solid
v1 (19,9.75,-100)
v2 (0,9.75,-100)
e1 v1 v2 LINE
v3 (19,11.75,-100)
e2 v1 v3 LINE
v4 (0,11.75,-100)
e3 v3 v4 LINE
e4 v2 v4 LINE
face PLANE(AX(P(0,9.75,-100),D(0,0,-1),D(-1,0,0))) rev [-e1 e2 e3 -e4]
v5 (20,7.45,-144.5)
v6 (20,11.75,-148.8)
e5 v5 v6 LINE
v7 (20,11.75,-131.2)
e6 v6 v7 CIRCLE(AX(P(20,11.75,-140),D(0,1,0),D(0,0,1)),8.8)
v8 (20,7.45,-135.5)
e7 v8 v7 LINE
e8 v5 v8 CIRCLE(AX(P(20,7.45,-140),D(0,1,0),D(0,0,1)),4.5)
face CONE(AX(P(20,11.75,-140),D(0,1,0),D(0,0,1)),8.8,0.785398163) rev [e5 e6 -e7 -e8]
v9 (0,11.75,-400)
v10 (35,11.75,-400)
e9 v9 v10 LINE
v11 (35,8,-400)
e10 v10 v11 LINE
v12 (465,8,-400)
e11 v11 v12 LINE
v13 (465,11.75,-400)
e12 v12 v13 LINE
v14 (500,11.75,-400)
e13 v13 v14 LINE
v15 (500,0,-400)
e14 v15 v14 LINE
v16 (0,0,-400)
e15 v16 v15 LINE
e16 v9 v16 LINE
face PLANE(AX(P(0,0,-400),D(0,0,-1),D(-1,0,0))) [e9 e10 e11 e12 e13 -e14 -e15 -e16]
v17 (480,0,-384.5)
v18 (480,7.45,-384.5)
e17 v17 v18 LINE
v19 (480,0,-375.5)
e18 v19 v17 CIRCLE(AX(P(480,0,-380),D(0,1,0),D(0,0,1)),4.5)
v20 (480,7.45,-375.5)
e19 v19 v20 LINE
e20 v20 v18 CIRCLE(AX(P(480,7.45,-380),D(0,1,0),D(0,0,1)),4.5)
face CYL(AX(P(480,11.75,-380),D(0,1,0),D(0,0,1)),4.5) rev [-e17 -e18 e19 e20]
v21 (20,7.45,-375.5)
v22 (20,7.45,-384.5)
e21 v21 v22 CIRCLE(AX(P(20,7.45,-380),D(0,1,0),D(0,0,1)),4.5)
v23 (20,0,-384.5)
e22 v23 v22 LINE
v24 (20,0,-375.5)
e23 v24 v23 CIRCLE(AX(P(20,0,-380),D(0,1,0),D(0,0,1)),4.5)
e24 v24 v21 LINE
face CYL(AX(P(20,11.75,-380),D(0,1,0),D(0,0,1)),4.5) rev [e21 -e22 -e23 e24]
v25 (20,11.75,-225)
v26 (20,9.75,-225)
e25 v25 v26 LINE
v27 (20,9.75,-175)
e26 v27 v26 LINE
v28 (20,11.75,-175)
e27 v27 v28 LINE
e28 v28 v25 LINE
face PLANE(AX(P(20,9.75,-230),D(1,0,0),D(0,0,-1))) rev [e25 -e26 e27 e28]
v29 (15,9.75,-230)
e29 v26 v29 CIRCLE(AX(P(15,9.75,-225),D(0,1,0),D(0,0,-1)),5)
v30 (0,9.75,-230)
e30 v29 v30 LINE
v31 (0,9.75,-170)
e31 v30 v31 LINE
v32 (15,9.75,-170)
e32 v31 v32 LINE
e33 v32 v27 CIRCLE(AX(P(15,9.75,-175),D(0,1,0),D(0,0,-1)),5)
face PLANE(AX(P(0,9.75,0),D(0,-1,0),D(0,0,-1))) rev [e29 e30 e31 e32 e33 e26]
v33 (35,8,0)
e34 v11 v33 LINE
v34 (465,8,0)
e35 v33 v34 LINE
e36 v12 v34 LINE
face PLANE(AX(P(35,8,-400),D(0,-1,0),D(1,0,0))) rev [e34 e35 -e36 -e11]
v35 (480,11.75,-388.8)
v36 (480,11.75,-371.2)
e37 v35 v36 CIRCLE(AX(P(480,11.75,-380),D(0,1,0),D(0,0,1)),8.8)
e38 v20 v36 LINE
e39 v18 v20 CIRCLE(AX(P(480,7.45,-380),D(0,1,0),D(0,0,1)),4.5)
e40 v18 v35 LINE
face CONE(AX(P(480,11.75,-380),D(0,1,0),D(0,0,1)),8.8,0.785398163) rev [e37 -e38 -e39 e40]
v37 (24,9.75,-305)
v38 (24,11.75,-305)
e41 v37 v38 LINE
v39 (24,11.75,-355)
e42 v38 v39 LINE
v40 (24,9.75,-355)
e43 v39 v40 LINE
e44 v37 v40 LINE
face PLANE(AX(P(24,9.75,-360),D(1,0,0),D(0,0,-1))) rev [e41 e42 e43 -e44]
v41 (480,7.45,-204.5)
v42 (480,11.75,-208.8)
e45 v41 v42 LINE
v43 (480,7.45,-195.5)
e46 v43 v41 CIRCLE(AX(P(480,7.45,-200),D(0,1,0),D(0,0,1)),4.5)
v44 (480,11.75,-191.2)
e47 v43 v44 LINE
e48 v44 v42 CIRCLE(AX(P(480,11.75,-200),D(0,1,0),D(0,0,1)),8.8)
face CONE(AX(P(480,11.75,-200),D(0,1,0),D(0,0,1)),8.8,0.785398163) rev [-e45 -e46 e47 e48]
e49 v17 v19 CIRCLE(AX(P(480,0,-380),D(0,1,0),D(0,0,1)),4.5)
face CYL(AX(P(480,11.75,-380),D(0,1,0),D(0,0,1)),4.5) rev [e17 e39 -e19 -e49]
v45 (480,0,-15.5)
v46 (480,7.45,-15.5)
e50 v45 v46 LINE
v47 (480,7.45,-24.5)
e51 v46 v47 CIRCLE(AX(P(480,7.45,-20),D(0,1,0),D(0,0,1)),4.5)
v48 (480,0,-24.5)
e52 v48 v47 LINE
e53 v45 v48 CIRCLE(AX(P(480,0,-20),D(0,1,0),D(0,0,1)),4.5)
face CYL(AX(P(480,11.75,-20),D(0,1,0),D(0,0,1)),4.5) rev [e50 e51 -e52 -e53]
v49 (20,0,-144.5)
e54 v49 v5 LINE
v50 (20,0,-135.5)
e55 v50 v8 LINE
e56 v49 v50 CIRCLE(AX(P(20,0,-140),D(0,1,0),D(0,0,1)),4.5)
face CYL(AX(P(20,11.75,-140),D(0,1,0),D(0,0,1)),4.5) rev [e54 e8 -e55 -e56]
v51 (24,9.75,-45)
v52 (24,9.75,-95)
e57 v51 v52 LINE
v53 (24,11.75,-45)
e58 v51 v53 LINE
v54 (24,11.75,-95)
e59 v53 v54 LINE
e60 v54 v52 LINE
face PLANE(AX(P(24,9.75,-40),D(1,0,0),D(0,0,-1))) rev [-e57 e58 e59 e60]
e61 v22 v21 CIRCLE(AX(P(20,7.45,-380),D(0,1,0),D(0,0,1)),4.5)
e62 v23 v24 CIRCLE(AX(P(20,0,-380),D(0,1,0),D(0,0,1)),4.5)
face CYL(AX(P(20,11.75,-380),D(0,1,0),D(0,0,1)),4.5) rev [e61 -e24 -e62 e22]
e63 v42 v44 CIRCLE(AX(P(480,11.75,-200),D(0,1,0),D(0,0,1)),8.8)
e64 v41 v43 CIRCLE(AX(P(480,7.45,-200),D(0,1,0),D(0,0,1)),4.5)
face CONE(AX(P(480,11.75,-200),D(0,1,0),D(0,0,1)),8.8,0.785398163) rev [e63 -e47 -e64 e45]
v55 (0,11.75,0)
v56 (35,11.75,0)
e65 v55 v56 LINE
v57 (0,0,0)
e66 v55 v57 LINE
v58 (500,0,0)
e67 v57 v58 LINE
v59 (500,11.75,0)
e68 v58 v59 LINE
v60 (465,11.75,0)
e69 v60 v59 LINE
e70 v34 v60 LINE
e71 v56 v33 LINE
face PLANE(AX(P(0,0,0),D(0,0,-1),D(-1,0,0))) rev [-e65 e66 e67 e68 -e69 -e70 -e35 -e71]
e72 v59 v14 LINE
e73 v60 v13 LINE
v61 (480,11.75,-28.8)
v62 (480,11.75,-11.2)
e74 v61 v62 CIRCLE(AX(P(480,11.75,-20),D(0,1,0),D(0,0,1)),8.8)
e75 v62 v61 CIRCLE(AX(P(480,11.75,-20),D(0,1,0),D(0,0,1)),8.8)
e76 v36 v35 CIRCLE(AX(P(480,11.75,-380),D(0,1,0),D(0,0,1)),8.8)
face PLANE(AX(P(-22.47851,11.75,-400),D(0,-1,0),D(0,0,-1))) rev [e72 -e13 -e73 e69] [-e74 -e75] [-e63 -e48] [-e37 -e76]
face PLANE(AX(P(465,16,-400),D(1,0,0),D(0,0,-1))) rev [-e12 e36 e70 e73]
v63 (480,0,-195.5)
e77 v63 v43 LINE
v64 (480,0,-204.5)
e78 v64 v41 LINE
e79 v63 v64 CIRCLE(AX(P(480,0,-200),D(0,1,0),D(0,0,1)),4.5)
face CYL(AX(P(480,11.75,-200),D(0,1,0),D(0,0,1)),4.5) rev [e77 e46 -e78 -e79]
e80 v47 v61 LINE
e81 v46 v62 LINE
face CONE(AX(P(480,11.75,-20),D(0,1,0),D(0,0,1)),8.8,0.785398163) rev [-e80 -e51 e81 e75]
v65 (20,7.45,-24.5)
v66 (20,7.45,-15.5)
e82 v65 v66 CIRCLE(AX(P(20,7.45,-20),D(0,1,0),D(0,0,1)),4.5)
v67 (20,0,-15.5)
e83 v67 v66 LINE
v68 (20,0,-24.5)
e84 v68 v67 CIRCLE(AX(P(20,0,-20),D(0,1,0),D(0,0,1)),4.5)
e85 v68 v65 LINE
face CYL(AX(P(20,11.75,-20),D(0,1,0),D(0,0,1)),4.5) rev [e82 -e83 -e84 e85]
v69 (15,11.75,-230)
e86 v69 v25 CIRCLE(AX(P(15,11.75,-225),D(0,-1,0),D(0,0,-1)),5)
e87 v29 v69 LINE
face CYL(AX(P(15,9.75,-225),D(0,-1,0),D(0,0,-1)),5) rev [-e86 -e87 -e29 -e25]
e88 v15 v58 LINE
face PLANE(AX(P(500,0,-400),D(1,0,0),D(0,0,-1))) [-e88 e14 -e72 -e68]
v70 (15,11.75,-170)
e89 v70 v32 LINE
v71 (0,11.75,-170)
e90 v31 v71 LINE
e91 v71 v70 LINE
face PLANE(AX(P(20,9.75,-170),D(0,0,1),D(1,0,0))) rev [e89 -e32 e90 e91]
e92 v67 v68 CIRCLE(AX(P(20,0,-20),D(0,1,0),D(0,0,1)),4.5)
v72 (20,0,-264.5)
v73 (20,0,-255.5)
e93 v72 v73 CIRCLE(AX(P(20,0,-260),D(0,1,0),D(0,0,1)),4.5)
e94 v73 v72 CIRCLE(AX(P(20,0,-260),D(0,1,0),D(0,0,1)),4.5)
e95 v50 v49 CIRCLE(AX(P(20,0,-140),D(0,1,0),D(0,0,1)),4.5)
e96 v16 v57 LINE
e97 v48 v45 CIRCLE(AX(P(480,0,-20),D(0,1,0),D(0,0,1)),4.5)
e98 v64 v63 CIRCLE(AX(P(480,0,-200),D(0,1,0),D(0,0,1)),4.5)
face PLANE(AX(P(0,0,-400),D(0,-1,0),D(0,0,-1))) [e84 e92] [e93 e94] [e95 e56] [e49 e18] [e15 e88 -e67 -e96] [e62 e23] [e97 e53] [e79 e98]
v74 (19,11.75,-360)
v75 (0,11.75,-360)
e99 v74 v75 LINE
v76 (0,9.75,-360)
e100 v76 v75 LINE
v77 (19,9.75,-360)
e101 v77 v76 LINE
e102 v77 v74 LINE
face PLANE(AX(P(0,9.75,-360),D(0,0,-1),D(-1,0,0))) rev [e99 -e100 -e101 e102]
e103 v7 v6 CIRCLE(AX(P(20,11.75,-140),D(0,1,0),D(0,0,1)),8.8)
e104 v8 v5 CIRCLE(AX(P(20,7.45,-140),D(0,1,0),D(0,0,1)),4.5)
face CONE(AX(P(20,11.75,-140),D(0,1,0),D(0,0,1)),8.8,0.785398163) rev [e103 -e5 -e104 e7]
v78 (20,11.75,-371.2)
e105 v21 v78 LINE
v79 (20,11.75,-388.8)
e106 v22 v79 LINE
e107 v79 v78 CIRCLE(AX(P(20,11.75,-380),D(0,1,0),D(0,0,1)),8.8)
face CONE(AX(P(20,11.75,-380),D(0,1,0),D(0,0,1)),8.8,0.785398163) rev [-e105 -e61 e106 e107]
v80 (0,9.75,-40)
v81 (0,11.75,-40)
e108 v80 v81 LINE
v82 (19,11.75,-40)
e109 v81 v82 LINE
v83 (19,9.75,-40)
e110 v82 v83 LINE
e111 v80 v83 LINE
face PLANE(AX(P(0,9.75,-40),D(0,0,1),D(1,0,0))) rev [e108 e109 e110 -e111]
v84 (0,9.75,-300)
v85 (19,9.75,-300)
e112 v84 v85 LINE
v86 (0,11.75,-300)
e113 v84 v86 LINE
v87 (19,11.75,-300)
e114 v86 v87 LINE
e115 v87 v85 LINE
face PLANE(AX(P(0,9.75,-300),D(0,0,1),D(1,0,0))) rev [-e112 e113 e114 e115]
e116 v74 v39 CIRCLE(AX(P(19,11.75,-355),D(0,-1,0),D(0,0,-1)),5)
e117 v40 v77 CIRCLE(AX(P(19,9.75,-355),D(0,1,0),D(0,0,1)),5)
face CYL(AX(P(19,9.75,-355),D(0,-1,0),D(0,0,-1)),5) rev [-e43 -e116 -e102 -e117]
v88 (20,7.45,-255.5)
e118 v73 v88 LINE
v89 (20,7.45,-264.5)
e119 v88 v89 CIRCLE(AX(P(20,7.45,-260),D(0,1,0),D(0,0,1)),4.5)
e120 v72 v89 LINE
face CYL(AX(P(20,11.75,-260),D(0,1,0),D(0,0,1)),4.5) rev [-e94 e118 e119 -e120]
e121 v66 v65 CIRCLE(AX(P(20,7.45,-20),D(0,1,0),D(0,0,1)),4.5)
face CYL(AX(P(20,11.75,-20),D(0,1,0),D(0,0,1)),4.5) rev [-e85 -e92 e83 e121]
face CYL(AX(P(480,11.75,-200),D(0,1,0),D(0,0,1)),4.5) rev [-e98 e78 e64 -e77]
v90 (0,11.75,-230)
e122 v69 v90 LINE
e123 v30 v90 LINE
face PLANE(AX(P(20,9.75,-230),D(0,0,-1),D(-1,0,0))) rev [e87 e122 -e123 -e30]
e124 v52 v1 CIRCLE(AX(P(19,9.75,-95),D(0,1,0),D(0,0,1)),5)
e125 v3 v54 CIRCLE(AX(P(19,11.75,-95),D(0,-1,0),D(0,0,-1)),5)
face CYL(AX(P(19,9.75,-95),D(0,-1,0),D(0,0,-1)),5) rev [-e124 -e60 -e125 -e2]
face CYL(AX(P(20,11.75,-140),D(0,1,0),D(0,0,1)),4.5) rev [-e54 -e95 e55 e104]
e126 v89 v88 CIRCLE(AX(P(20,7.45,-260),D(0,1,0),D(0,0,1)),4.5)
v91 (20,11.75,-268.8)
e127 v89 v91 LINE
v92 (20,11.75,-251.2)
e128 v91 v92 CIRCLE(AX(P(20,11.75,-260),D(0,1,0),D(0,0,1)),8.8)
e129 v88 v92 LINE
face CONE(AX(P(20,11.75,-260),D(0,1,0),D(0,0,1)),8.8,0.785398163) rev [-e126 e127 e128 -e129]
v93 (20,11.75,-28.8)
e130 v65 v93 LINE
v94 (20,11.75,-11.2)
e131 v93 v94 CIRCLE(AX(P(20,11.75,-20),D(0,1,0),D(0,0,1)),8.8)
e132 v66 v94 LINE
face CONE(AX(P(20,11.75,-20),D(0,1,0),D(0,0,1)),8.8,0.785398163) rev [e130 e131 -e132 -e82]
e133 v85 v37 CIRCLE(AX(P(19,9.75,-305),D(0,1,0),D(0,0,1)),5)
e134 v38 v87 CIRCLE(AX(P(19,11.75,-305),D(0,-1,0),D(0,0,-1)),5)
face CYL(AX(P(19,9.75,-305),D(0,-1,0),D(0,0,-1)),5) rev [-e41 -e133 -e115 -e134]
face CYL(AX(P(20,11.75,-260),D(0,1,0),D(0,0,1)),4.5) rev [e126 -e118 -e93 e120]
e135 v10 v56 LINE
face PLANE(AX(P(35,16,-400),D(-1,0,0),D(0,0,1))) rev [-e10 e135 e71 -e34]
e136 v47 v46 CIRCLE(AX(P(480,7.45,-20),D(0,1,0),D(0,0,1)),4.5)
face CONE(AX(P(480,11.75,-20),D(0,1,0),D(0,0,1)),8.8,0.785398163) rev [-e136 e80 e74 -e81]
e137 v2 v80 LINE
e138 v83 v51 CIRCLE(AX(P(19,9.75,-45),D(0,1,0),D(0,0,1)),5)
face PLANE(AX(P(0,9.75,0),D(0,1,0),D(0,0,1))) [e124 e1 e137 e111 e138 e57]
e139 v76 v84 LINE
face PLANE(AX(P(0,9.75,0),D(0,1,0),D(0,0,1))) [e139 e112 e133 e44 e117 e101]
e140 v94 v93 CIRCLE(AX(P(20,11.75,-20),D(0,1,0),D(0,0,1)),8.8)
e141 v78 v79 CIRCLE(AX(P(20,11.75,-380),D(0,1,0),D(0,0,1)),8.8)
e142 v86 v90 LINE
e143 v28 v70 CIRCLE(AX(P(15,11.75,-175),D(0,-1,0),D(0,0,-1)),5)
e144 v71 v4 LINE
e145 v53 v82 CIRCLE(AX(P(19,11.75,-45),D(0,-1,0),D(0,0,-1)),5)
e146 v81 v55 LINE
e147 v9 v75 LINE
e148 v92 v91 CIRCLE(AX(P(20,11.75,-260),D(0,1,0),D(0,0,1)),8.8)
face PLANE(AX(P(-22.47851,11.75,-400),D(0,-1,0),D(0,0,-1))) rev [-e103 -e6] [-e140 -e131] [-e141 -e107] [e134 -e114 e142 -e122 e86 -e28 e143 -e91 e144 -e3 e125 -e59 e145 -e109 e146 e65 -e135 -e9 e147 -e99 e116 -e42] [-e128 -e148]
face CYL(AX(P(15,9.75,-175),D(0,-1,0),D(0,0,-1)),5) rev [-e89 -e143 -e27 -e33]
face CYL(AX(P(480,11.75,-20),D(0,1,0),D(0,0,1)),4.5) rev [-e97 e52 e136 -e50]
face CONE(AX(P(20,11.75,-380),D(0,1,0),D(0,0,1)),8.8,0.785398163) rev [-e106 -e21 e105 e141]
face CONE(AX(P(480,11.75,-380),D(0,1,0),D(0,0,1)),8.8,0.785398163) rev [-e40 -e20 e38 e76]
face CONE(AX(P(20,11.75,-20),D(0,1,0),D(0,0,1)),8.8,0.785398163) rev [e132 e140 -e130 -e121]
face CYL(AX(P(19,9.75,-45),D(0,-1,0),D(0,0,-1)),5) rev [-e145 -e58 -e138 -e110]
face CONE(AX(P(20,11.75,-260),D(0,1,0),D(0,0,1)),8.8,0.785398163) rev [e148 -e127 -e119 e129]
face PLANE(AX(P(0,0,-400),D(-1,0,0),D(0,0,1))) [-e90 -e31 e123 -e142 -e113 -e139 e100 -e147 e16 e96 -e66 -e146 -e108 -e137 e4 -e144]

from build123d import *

# Parameters (mm, degrees)
SKETCH1_W                                           = 500
SKETCH1_H                                           = 24
BOSS_EXTRUDE1_DEPTH                                 = 400
SKETCH2_W                                           = 430
SKETCH2_H                                           = 8
CUT_EXTRUDE1_DEPTH                                  = 641.762046317
SKETCH3_W                                           = 544.957019416
SKETCH3_H                                           = 0.5
CUT_EXTRUDE2_DEPTH                                  = 641.762046317
SKETCH12_W                                          = 569.007892772
SKETCH12_H                                          = 39.328779912
CUT_EXTRUDE3_DEPTH                                  = 641.762046317
HOLE_WIZARD_HEX_SOCKET_SEMI_COUNTERSUNK_D           = 9
HOLE_WIZARD_HEX_SOCKET_SEMI_COUNTERSUNK_CSINK_D     = 17.6
HOLE_WIZARD_HEX_SOCKET_SEMI_COUNTERSUNK_CSINK_ANGLE = 90
SKETCH16_W                                          = 24
SKETCH16_H                                          = 60
SKETCH16_W_2                                        = 20
CUT_EXTRUDE4_DEPTH                                  = 2
FILLET1_R                                           = 5
HOLE_WIZARD_HEX_SOCKET_SEMI_COUNTER_2_D             = 9
HOLE_WIZARD_HEX_SOCKET_SEMI_COUNTER_2_CSINK_D       = 17.6
HOLE_WIZARD_HEX_SOCKET_SEMI_COUNTER_2_CSINK_ANGLE   = 90


with BuildPart() as part:
    # Sketch1 → Boss-Extrude1 (new body)
    with BuildSketch(Plane.XY):
        with Locations((250, 12)):
            Rectangle(SKETCH1_W, SKETCH1_H)
    extrude(amount=-BOSS_EXTRUDE1_DEPTH)

    # Sketch2 → Cut-Extrude1 (cut, through all)
    with BuildSketch(Plane.XY):
        with Locations((250, 12)):
            Rectangle(SKETCH2_W, SKETCH2_H)
    extrude(amount=-CUT_EXTRUDE1_DEPTH, mode=Mode.SUBTRACT)

    # Sketch3 → Cut-Extrude2 (cut, through all)
    with BuildSketch(Plane.XY):
        with Locations((250, 12)):
            Rectangle(SKETCH3_W, SKETCH3_H)
    extrude(amount=-CUT_EXTRUDE2_DEPTH, mode=Mode.SUBTRACT)


with BuildPart() as cut_extrude2_piece_1:
    # of the separate pieces the step leaves, piece 1, a body of its own (cut_extrude2_pieces)
    add(part.part.solids().sort_by_distance((0, 0, 0))[0])

    # Hole wizard_ hex socket semi-countersunk (through all)
    with Locations(Plane(origin=(0, 11.75, 0), x_dir=(1, 0, 0), z_dir=(0, 1, 0))):
        with Locations((20, 20), (480, 20), (20, 380), (480, 380)):
            CounterSinkHole(HOLE_WIZARD_HEX_SOCKET_SEMI_COUNTERSUNK_D / 2, HOLE_WIZARD_HEX_SOCKET_SEMI_COUNTERSUNK_CSINK_D / 2, counter_sink_angle=HOLE_WIZARD_HEX_SOCKET_SEMI_COUNTERSUNK_CSINK_ANGLE)

    # Sketch16 → Cut-Extrude4 (cut)
    with BuildSketch(Plane(origin=(0, 11.75, 0), x_dir=(1, 0, 0), z_dir=(0, 1, 0))):
        with Locations((12, 330)):
            Rectangle(SKETCH16_W, SKETCH16_H)
        with Locations((12, 70)):
            Rectangle(SKETCH16_W, SKETCH16_H)
        with Locations((10, 200)):
            Rectangle(SKETCH16_W_2, SKETCH16_H)
    extrude(amount=-CUT_EXTRUDE4_DEPTH, mode=Mode.SUBTRACT)

    # Fillet1
    fillet1_edges = [cut_extrude2_piece_1.edges().sort_by_distance(p)[0] for p in [
        (24, 10.75, -360),
        (24, 10.75, -300),
        (24, 10.75, -40),
        (24, 10.75, -100),
        (20, 10.75, -230),
        (20, 10.75, -170),
    ]]
    fillet(fillet1_edges, radius=FILLET1_R)

    # Hole wizard_ hex socket semi-counter 2 (through all)
    with Locations(Plane(origin=(0, 11.75, 0), x_dir=(1, 0, 0), z_dir=(0, 1, 0))):
        with Locations((20, 140), (20, 260), (480, 200)):
            CounterSinkHole(HOLE_WIZARD_HEX_SOCKET_SEMI_COUNTER_2_D / 2, HOLE_WIZARD_HEX_SOCKET_SEMI_COUNTER_2_CSINK_D / 2, counter_sink_angle=HOLE_WIZARD_HEX_SOCKET_SEMI_COUNTER_2_CSINK_ANGLE)


with BuildPart() as cut_extrude2_piece_2:
    # of the separate pieces the step leaves, piece 2, a body of its own (cut_extrude2_pieces)
    add(part.part.solids().sort_by_distance((0, 24, 0))[0])

    # Sketch12 → Cut-Extrude3 (cut, through all)
    with BuildSketch(Plane.XY):
        with Locations((265.175540793, 31.664389956)):
            Rectangle(SKETCH12_W, SKETCH12_H)
    extrude(amount=-CUT_EXTRUDE3_DEPTH, mode=Mode.SUBTRACT)


solid = cut_extrude2_piece_1.part
